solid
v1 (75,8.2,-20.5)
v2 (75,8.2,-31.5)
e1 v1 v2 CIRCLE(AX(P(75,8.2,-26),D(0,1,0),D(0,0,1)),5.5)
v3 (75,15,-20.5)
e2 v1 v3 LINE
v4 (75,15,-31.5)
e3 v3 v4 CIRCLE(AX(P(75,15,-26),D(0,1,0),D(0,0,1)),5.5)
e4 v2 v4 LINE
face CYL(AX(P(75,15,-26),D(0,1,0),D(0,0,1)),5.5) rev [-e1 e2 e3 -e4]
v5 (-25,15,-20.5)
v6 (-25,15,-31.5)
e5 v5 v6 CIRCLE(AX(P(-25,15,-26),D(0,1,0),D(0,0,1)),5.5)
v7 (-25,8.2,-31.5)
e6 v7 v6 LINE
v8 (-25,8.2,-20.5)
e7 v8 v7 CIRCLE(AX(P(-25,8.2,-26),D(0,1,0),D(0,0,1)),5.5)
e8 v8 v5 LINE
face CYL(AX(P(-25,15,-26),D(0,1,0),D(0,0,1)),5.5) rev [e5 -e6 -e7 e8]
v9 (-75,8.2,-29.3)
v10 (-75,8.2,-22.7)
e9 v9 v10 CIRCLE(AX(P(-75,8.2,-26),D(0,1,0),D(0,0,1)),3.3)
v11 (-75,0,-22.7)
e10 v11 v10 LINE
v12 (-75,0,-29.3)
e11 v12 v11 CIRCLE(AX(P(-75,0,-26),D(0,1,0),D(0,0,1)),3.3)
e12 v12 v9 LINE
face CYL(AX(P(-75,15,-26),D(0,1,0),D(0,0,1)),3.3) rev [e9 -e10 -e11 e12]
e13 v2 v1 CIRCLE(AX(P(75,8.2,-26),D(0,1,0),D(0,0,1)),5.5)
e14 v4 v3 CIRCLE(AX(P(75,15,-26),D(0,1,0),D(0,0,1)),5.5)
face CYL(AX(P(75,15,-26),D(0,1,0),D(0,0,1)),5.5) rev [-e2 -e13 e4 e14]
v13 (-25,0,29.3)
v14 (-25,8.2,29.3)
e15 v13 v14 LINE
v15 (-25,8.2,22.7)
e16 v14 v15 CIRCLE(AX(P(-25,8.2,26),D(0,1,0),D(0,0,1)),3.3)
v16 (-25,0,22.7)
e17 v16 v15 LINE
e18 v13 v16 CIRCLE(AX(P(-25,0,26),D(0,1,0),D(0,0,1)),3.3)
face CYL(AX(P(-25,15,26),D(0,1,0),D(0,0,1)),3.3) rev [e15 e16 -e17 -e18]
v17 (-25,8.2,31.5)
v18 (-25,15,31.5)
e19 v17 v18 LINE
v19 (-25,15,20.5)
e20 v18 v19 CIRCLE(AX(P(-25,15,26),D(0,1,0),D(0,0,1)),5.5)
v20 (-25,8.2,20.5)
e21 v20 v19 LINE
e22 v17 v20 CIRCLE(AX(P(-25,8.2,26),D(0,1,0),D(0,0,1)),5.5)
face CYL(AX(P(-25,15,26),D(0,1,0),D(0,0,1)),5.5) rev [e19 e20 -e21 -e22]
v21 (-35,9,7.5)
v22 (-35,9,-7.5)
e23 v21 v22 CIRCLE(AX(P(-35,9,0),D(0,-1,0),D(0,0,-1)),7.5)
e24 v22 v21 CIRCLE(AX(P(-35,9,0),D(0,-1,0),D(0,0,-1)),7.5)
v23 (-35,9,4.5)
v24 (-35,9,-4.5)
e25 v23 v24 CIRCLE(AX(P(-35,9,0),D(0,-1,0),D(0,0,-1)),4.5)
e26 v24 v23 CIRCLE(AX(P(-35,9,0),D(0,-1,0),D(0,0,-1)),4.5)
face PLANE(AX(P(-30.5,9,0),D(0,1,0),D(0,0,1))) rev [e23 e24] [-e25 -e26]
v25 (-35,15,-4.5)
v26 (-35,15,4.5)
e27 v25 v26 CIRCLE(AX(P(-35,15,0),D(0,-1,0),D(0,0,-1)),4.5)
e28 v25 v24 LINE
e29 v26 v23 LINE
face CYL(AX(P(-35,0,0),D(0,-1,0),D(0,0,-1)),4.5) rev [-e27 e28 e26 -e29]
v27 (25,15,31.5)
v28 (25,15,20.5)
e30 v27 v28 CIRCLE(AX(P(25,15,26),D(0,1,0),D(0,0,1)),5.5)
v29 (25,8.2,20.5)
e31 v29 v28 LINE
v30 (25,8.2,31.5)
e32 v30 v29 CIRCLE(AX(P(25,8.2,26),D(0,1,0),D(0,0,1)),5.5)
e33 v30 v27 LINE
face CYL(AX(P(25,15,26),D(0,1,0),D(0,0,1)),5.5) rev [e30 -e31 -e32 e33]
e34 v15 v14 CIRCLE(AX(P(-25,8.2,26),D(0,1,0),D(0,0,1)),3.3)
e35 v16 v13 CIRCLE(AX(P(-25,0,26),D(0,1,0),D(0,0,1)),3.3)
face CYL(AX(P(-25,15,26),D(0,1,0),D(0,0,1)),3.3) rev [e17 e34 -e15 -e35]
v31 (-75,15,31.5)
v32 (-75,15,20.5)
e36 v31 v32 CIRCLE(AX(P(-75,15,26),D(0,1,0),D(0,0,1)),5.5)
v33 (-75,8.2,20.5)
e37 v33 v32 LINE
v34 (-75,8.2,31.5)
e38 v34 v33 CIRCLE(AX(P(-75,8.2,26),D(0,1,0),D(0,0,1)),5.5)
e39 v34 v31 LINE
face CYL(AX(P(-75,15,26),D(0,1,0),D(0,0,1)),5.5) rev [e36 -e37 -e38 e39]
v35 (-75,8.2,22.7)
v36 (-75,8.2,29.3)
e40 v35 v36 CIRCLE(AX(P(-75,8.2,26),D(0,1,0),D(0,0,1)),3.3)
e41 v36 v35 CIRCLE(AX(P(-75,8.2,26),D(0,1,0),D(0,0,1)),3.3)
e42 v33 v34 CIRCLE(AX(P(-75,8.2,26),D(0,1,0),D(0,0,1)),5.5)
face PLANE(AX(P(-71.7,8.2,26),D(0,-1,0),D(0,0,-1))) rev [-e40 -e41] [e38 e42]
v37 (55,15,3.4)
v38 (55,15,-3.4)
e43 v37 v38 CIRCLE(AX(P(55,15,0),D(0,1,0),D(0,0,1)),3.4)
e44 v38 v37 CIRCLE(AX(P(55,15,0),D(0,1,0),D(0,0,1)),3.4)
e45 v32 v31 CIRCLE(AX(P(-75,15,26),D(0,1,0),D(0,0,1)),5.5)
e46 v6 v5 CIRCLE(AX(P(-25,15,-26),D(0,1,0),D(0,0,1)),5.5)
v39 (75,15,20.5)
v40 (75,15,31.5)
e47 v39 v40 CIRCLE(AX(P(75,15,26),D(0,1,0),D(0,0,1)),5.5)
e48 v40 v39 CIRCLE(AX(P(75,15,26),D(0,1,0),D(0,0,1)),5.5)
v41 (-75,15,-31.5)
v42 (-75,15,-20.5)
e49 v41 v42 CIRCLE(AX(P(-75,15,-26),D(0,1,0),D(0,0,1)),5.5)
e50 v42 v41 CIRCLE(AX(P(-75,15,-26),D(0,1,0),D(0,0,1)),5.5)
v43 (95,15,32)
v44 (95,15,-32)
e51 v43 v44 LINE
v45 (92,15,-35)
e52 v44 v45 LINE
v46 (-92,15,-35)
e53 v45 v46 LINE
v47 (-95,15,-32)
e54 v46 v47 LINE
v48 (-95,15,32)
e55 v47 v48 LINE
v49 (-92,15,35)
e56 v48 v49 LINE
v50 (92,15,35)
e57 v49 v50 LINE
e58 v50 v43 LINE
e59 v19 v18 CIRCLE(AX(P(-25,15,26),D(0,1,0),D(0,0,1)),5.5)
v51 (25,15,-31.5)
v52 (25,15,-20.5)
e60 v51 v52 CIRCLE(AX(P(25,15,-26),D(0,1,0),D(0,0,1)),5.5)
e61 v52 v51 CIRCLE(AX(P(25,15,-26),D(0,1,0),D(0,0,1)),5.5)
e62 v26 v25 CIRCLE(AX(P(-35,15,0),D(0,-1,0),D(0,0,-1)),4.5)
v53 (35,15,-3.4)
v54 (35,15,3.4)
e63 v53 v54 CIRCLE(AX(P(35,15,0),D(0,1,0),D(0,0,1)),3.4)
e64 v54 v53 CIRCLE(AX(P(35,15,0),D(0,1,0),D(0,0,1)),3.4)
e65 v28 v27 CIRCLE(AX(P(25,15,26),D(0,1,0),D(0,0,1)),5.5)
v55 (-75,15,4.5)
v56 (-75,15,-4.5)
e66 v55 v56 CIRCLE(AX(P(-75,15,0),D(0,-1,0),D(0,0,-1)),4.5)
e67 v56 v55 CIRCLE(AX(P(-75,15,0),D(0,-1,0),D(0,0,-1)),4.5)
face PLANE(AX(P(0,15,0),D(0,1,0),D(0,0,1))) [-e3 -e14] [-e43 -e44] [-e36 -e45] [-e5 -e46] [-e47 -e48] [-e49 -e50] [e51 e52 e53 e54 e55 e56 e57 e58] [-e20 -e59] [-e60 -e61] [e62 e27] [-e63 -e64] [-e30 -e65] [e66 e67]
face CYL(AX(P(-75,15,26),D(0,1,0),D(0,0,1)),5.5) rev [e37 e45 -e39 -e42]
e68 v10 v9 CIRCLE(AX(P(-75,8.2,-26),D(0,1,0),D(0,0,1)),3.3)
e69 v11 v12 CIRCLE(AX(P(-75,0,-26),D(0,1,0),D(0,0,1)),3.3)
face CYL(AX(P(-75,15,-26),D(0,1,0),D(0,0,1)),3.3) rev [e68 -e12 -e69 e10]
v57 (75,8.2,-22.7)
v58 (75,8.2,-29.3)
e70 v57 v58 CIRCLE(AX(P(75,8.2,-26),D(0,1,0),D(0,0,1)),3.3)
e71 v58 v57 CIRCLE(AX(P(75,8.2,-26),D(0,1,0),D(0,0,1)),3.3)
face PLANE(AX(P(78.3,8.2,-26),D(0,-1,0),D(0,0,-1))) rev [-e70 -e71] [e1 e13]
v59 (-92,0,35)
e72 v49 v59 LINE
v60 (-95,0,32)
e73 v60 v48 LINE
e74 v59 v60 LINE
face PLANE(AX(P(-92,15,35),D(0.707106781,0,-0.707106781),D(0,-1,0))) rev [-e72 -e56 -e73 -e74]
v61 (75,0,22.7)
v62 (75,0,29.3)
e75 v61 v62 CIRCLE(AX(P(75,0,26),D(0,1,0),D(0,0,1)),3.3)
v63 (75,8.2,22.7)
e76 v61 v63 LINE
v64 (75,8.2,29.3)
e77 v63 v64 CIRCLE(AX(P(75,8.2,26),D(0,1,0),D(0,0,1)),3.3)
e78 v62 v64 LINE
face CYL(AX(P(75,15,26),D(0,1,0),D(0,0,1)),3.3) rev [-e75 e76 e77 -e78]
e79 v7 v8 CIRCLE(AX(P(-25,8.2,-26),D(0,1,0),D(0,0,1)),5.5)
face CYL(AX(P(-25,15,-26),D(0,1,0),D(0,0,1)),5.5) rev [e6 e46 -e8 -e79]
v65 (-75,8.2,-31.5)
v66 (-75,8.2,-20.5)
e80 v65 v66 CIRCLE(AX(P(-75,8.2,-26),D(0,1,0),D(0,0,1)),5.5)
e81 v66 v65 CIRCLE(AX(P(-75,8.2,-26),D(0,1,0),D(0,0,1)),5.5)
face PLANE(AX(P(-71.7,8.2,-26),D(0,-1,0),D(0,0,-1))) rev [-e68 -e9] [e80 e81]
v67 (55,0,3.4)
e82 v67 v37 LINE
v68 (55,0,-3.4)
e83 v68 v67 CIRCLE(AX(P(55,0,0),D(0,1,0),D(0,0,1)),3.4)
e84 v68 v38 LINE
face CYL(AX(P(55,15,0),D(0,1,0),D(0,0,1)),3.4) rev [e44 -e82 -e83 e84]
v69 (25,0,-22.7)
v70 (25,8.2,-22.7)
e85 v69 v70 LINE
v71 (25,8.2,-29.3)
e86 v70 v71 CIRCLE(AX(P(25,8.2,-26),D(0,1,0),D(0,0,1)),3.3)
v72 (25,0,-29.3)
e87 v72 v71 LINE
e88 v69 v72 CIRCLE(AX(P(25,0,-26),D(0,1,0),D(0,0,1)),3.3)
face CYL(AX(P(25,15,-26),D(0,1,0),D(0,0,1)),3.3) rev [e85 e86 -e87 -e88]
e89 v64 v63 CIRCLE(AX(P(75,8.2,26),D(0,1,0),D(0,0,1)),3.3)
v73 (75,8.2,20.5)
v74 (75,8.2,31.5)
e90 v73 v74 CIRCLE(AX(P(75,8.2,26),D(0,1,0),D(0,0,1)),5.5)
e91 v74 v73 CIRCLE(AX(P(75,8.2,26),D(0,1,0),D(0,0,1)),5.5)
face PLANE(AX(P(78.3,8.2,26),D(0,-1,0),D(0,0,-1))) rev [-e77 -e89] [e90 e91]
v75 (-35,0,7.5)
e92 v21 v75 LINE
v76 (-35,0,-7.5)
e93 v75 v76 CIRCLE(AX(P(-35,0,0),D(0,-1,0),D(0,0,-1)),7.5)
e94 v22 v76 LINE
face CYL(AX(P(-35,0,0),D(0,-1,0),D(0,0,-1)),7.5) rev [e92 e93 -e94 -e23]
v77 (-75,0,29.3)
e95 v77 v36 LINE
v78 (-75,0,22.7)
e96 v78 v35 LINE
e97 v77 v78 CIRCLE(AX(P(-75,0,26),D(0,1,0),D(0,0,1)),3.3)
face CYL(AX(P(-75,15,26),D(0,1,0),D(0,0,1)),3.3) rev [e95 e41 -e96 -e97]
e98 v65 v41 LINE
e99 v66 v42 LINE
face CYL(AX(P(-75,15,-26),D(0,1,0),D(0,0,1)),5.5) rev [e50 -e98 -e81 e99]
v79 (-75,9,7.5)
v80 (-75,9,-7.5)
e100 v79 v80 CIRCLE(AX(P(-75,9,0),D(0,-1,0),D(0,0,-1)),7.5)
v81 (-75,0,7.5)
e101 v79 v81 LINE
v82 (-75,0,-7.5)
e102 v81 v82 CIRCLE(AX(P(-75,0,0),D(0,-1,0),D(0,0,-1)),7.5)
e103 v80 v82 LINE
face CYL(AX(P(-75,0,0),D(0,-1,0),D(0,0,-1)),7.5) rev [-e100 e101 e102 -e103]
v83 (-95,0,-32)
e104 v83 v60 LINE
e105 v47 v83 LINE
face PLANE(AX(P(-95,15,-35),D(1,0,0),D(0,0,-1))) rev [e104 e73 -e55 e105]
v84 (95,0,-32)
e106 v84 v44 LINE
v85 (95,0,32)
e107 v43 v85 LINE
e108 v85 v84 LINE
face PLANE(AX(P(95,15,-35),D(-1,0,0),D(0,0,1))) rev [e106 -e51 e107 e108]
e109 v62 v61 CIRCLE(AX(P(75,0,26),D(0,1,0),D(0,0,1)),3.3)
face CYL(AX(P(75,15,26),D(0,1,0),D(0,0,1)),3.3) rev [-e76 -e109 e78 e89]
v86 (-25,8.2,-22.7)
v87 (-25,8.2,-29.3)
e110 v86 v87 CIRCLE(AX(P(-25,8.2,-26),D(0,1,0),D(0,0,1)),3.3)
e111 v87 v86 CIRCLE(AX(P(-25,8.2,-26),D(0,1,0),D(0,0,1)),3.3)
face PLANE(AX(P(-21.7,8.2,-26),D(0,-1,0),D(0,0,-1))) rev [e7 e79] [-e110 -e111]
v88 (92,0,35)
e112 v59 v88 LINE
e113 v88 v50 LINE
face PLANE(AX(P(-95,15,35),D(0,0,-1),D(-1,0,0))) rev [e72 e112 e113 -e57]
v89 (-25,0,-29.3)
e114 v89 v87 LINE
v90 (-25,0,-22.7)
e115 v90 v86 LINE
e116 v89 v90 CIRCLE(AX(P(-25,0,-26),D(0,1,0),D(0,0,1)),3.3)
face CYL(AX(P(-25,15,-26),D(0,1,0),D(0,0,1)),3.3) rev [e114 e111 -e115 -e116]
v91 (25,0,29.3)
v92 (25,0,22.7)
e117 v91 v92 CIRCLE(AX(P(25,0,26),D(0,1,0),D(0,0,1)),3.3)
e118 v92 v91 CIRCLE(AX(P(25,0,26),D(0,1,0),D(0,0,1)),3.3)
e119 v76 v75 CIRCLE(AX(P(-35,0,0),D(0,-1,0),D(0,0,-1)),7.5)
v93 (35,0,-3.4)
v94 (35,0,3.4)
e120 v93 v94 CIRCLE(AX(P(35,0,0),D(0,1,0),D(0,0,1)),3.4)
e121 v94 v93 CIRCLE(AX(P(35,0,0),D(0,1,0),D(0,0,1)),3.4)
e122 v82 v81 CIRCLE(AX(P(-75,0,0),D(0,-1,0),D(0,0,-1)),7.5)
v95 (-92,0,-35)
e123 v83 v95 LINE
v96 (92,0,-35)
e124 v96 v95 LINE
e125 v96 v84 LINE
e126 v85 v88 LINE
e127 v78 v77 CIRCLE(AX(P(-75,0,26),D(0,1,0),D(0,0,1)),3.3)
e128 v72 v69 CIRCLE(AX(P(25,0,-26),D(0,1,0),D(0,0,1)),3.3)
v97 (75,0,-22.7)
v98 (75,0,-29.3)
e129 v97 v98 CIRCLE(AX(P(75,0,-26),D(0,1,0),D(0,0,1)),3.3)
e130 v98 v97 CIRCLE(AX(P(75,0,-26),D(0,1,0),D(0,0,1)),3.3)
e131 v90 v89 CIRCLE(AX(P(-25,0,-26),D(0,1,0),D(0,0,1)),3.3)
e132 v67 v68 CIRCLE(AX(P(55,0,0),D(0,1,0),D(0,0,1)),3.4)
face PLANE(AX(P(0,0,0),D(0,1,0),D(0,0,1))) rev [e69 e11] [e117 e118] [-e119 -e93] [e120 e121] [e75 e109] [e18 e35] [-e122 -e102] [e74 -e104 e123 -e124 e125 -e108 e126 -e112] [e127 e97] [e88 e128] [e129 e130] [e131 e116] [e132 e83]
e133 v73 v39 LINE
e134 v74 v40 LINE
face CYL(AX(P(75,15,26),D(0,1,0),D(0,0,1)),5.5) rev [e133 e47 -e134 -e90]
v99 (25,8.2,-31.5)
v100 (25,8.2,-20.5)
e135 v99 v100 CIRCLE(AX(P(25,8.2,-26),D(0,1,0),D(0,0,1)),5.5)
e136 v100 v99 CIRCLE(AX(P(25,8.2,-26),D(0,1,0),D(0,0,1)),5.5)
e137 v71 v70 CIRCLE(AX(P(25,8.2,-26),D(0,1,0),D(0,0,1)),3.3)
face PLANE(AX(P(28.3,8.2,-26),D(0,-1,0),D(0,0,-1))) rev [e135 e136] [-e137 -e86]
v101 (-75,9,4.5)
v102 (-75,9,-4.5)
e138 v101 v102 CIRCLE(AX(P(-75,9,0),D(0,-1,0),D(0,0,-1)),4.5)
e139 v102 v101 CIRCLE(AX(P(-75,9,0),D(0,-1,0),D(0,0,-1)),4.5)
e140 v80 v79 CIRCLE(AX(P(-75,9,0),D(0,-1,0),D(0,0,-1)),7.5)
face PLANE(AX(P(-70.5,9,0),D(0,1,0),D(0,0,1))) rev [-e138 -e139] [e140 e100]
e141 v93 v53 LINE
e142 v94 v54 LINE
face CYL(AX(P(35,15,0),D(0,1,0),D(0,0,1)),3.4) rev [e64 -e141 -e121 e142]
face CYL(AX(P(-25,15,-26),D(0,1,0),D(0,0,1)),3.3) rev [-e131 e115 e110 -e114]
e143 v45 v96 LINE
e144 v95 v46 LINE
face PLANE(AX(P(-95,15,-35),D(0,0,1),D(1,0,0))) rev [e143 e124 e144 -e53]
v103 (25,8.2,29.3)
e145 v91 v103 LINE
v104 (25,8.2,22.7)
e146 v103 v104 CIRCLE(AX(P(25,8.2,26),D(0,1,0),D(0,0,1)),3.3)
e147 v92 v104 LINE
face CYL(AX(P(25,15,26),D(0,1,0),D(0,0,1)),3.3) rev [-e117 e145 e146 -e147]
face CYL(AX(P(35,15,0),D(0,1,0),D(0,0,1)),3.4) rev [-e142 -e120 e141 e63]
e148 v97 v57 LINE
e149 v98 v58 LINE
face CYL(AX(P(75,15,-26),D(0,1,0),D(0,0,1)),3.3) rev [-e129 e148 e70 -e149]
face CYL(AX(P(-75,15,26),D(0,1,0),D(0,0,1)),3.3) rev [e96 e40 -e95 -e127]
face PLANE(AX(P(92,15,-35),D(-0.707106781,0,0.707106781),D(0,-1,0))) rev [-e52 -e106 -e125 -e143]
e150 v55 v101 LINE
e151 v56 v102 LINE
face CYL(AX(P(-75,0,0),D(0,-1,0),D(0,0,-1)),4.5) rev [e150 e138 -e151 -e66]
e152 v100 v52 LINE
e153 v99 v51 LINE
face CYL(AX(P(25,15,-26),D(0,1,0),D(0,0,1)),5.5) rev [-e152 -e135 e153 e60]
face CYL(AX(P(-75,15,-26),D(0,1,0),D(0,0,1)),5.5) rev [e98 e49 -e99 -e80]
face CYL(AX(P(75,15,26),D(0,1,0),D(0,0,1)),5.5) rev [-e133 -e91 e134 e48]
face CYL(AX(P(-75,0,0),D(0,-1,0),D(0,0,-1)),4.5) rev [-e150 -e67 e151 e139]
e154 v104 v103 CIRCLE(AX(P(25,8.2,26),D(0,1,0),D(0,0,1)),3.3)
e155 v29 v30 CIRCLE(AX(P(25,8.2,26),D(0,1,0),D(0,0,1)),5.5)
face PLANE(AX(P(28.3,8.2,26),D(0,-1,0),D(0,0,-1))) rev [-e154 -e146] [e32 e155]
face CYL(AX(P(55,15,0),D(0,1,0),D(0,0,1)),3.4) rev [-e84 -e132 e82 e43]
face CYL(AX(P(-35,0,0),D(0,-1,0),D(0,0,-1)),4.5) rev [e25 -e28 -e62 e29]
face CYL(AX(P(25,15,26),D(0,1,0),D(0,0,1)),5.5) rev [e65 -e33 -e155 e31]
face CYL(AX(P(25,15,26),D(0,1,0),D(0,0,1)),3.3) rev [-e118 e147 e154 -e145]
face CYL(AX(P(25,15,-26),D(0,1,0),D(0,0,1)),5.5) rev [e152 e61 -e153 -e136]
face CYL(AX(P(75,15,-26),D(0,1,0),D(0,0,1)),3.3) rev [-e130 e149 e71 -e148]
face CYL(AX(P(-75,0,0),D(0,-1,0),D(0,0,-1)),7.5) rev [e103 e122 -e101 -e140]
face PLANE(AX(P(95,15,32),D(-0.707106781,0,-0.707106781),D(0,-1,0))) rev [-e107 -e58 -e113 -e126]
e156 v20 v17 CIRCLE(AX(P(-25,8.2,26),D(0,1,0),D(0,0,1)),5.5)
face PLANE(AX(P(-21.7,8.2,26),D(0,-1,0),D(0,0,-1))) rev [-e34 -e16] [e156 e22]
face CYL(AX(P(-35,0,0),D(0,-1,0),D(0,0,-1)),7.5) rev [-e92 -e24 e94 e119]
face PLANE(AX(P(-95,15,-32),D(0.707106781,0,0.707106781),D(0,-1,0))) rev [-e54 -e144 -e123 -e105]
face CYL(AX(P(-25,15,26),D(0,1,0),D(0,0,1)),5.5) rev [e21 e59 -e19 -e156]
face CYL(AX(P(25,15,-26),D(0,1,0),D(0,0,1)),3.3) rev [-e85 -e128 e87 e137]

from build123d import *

# Parameters (mm, degrees)
SKETCH_1_W                = 190
SKETCH_1_H                = 70
EXTRUDE_1_DEPTH           = 15
CHAMFER_1_SIZE            = 3
HOLE_WIZARD_5_D           = 6.6
HOLE_WIZARD_5_CBORE_D     = 11
HOLE_WIZARD_5_CBORE_DEPTH = 6.8
HOLE_WIZARD_3_D           = 9
HOLE_WIZARD_3_CBORE_D     = 15
HOLE_WIZARD_3_CBORE_DEPTH = 9
HOLE_WIZARD_M8_1_D        = 6.8


with BuildPart() as part:
    # 草图1 → 凸台-拉伸1 (new body)
    with BuildSketch(Plane(origin=(0, 0, 0), x_dir=(1, 0, 0), z_dir=(0, 1, 0))):
        Rectangle(SKETCH_1_W, SKETCH_1_H)
    extrude(amount=EXTRUDE_1_DEPTH)

    # 倒角1
    chamfer_1_edges = [part.edges().sort_by_distance(p)[0] for p in [
        (95, 7.5, 35),
        (-95, 7.5, 35),
        (-95, 7.5, -35),
        (95, 7.5, -35),
    ]]
    chamfer(chamfer_1_edges, length=CHAMFER_1_SIZE)

    # 打孔尺寸(%根据)内六角圆柱头螺钉的类型5 (through all)
    with Locations(Plane(origin=(0, 15, 0), x_dir=(1, 0, 0), z_dir=(0, 1, 0))):
        with Locations((75, -26), (25, -26), (-25, -26), (-75, -26), (25, 26), (-25, 26), (-75, 26), (75, 26)):
            CounterBoreHole(HOLE_WIZARD_5_D / 2, HOLE_WIZARD_5_CBORE_D / 2, HOLE_WIZARD_5_CBORE_DEPTH)

    # 打孔尺寸(%根据)内六角圆柱头螺钉的类型3 (through all)
    with Locations(Plane(origin=(0, 0, 0), x_dir=(-1, 0, 0), z_dir=(0, -1, 0))):
        with Locations((35, 0), (75, 0)):
            CounterBoreHole(HOLE_WIZARD_3_D / 2, HOLE_WIZARD_3_CBORE_D / 2, HOLE_WIZARD_3_CBORE_DEPTH)

    # M8 螺纹孔1 (through all)
    with Locations(Plane(origin=(0, 15, 0), x_dir=(1, 0, 0), z_dir=(0, 1, 0))):
        with Locations((55, 0), (35, 0)):
            Hole(HOLE_WIZARD_M8_1_D / 2)


solid = part.part
